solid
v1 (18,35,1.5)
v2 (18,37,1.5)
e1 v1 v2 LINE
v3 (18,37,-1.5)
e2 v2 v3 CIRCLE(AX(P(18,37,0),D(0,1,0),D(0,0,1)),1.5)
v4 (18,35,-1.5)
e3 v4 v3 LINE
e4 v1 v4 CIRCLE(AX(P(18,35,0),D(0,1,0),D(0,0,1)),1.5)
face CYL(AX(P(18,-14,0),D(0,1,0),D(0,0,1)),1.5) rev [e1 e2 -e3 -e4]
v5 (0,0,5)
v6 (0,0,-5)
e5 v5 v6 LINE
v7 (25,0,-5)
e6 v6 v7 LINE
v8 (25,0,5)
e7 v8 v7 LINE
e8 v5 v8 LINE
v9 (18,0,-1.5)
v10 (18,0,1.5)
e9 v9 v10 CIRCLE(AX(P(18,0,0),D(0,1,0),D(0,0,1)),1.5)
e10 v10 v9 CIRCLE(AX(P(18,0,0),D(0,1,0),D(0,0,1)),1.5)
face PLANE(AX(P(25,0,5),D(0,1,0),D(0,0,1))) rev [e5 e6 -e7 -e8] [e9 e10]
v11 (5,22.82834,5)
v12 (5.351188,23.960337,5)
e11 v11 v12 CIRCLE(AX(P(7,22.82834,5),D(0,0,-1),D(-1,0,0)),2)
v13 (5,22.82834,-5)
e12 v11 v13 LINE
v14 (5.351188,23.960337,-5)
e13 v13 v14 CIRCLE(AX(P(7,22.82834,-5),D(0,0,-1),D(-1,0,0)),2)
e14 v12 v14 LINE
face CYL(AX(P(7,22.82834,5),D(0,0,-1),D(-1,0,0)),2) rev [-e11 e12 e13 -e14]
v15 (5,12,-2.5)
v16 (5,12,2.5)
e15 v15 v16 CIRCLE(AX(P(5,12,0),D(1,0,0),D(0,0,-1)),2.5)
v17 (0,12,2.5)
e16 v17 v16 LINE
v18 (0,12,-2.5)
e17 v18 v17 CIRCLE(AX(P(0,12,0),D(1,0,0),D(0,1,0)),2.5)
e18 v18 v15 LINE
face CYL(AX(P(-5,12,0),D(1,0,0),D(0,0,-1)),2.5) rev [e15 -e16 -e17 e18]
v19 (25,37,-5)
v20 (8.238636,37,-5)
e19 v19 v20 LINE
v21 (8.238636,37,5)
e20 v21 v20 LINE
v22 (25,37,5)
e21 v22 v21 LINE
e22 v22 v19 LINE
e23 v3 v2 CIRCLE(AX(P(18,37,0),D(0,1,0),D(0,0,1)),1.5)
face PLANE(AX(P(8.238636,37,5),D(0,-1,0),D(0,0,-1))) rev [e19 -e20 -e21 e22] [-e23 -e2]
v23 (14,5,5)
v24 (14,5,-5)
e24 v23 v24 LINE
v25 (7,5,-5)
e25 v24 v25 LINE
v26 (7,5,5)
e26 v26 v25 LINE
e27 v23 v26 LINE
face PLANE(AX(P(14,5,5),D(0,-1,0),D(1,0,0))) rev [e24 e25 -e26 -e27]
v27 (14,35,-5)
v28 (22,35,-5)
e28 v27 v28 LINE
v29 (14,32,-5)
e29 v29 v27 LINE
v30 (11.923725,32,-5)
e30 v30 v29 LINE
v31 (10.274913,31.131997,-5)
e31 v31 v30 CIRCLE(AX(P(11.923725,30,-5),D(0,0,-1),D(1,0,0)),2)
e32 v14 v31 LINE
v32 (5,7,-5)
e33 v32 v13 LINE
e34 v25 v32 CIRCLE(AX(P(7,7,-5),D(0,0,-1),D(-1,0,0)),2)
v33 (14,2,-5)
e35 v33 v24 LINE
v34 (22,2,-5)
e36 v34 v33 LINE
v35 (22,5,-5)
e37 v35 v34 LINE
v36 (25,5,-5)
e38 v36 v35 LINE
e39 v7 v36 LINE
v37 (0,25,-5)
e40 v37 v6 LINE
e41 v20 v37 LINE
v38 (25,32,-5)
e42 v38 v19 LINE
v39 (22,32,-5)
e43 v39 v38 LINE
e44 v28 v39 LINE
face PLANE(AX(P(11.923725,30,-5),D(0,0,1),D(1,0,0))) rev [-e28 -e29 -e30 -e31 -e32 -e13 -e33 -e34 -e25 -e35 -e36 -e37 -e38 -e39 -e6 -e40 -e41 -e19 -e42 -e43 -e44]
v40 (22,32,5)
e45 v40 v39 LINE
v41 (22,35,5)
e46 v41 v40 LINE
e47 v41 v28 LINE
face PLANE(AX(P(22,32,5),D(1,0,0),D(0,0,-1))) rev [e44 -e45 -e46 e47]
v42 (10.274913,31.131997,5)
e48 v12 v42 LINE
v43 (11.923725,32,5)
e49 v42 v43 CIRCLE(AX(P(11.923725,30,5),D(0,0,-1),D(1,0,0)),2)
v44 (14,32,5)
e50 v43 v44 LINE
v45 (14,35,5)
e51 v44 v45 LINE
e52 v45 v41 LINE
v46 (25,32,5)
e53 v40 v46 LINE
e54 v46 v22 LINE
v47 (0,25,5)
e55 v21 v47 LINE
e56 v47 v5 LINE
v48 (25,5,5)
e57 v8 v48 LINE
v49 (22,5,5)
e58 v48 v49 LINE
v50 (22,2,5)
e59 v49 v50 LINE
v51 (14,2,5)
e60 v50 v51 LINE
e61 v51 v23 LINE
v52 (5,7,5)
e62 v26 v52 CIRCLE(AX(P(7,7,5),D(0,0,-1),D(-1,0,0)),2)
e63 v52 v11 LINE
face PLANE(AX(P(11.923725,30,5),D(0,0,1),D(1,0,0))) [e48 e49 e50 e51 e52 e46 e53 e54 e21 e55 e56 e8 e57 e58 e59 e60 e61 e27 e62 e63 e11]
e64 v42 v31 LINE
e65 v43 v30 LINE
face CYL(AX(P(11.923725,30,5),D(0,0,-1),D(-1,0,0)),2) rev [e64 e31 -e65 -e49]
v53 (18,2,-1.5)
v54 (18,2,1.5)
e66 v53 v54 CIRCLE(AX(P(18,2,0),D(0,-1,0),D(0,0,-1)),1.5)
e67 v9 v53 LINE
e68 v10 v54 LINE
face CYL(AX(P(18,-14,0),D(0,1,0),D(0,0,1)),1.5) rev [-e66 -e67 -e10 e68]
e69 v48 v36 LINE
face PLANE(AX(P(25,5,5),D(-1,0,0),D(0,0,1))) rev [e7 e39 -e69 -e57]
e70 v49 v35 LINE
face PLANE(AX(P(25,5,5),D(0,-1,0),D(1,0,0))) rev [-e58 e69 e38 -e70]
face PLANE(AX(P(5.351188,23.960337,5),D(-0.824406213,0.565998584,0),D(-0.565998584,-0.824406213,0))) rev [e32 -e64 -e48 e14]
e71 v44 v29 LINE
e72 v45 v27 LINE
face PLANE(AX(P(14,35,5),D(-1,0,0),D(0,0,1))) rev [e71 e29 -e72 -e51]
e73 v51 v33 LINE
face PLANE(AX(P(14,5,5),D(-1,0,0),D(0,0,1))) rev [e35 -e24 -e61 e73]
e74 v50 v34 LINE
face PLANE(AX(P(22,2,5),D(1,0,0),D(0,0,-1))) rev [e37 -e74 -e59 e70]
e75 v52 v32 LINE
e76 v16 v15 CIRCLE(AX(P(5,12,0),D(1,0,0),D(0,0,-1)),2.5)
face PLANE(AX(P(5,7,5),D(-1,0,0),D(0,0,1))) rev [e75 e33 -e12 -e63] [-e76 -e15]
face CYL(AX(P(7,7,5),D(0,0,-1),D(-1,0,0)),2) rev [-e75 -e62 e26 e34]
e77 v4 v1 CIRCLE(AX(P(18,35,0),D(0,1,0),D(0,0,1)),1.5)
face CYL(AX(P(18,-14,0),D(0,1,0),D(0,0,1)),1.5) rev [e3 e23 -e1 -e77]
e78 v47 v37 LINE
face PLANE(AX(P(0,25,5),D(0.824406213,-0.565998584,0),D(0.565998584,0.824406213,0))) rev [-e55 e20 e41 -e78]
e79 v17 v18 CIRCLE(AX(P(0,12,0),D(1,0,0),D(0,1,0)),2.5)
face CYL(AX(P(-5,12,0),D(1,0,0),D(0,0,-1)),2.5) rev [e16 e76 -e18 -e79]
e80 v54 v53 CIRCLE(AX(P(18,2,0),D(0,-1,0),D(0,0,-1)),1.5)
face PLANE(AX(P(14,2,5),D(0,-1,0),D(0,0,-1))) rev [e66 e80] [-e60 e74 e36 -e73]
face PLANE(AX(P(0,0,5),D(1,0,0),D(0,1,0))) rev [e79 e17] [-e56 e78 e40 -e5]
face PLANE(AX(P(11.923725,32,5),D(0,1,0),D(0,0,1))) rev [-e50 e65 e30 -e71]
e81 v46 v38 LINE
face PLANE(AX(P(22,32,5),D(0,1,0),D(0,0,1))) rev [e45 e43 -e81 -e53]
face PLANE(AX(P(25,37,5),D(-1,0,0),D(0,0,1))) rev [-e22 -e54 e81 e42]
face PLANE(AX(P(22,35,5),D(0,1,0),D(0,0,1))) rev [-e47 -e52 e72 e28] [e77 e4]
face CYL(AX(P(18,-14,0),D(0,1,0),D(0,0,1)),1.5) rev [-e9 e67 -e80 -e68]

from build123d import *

# Parameters (mm, degrees)
C_BRACKET_BODY_DEPTH      = 5
WEB_HOLE_SKETCH_R         = 2.5
WEB_HOLE_DEPTH            = 10
FLANGE_HOLE_SKETCH_R      = 1.5
FLANGE_THROUGH_HOLE_DEPTH = 51


with BuildPart() as part:
    # Bracket Profile Sketch → C Bracket Body (new, symmetric)
    with BuildSketch(Plane.XY):
        with BuildLine():
            Line((0, 0), (0, 25))
            Line((0, 25), (8.238636364, 37))
            Line((8.238636364, 37), (25, 37))
            Line((25, 37), (25, 32))
            Line((25, 32), (22, 32))
            Line((22, 32), (22, 35))
            Line((22, 35), (14, 35))
            Line((14, 35), (14, 32))
            Line((14, 32), (11.923724939, 32))
            ThreePointArc((11.923724939, 32), (10.992058242, 31.769744944), (10.274912513, 31.131997167))
            Line((10.274912513, 31.131997167), (5.351187575, 23.960337118))
            ThreePointArc((5.351187575, 23.960337118), (5.08981351, 23.420950764), (5, 22.828339951))
            Line((5, 22.828339951), (5, 7))
            ThreePointArc((5, 7), (5.585786438, 5.585786438), (7, 5))
            Line((7, 5), (14, 5))
            Line((14, 5), (14, 2))
            Line((14, 2), (22, 2))
            Line((22, 2), (22, 5))
            Line((22, 5), (25, 5))
            Line((25, 5), (25, 0))
            Line((25, 0), (0, 0))
        make_face()
    extrude(amount=C_BRACKET_BODY_DEPTH, both=True)

    # Web Hole Sketch → Web Hole (cut)
    with BuildSketch(Plane(origin=(5, 0, 0), x_dir=(0, 0, -1), z_dir=(1, 0, 0))):
        with Locations((0, 12)):
            Circle(WEB_HOLE_SKETCH_R)
    extrude(amount=-WEB_HOLE_DEPTH, mode=Mode.SUBTRACT)

    # Flange Hole Sketch → Flange Through Hole (cut)
    with BuildSketch(Plane(origin=(0, 37, 0), x_dir=(1, 0, 0), z_dir=(0, 1, 0))):
        with Locations(Location((18, 0, 0), (0, 0, 270))):
            Circle(FLANGE_HOLE_SKETCH_R)
    extrude(amount=-FLANGE_THROUGH_HOLE_DEPTH, mode=Mode.SUBTRACT)


solid = part.part
